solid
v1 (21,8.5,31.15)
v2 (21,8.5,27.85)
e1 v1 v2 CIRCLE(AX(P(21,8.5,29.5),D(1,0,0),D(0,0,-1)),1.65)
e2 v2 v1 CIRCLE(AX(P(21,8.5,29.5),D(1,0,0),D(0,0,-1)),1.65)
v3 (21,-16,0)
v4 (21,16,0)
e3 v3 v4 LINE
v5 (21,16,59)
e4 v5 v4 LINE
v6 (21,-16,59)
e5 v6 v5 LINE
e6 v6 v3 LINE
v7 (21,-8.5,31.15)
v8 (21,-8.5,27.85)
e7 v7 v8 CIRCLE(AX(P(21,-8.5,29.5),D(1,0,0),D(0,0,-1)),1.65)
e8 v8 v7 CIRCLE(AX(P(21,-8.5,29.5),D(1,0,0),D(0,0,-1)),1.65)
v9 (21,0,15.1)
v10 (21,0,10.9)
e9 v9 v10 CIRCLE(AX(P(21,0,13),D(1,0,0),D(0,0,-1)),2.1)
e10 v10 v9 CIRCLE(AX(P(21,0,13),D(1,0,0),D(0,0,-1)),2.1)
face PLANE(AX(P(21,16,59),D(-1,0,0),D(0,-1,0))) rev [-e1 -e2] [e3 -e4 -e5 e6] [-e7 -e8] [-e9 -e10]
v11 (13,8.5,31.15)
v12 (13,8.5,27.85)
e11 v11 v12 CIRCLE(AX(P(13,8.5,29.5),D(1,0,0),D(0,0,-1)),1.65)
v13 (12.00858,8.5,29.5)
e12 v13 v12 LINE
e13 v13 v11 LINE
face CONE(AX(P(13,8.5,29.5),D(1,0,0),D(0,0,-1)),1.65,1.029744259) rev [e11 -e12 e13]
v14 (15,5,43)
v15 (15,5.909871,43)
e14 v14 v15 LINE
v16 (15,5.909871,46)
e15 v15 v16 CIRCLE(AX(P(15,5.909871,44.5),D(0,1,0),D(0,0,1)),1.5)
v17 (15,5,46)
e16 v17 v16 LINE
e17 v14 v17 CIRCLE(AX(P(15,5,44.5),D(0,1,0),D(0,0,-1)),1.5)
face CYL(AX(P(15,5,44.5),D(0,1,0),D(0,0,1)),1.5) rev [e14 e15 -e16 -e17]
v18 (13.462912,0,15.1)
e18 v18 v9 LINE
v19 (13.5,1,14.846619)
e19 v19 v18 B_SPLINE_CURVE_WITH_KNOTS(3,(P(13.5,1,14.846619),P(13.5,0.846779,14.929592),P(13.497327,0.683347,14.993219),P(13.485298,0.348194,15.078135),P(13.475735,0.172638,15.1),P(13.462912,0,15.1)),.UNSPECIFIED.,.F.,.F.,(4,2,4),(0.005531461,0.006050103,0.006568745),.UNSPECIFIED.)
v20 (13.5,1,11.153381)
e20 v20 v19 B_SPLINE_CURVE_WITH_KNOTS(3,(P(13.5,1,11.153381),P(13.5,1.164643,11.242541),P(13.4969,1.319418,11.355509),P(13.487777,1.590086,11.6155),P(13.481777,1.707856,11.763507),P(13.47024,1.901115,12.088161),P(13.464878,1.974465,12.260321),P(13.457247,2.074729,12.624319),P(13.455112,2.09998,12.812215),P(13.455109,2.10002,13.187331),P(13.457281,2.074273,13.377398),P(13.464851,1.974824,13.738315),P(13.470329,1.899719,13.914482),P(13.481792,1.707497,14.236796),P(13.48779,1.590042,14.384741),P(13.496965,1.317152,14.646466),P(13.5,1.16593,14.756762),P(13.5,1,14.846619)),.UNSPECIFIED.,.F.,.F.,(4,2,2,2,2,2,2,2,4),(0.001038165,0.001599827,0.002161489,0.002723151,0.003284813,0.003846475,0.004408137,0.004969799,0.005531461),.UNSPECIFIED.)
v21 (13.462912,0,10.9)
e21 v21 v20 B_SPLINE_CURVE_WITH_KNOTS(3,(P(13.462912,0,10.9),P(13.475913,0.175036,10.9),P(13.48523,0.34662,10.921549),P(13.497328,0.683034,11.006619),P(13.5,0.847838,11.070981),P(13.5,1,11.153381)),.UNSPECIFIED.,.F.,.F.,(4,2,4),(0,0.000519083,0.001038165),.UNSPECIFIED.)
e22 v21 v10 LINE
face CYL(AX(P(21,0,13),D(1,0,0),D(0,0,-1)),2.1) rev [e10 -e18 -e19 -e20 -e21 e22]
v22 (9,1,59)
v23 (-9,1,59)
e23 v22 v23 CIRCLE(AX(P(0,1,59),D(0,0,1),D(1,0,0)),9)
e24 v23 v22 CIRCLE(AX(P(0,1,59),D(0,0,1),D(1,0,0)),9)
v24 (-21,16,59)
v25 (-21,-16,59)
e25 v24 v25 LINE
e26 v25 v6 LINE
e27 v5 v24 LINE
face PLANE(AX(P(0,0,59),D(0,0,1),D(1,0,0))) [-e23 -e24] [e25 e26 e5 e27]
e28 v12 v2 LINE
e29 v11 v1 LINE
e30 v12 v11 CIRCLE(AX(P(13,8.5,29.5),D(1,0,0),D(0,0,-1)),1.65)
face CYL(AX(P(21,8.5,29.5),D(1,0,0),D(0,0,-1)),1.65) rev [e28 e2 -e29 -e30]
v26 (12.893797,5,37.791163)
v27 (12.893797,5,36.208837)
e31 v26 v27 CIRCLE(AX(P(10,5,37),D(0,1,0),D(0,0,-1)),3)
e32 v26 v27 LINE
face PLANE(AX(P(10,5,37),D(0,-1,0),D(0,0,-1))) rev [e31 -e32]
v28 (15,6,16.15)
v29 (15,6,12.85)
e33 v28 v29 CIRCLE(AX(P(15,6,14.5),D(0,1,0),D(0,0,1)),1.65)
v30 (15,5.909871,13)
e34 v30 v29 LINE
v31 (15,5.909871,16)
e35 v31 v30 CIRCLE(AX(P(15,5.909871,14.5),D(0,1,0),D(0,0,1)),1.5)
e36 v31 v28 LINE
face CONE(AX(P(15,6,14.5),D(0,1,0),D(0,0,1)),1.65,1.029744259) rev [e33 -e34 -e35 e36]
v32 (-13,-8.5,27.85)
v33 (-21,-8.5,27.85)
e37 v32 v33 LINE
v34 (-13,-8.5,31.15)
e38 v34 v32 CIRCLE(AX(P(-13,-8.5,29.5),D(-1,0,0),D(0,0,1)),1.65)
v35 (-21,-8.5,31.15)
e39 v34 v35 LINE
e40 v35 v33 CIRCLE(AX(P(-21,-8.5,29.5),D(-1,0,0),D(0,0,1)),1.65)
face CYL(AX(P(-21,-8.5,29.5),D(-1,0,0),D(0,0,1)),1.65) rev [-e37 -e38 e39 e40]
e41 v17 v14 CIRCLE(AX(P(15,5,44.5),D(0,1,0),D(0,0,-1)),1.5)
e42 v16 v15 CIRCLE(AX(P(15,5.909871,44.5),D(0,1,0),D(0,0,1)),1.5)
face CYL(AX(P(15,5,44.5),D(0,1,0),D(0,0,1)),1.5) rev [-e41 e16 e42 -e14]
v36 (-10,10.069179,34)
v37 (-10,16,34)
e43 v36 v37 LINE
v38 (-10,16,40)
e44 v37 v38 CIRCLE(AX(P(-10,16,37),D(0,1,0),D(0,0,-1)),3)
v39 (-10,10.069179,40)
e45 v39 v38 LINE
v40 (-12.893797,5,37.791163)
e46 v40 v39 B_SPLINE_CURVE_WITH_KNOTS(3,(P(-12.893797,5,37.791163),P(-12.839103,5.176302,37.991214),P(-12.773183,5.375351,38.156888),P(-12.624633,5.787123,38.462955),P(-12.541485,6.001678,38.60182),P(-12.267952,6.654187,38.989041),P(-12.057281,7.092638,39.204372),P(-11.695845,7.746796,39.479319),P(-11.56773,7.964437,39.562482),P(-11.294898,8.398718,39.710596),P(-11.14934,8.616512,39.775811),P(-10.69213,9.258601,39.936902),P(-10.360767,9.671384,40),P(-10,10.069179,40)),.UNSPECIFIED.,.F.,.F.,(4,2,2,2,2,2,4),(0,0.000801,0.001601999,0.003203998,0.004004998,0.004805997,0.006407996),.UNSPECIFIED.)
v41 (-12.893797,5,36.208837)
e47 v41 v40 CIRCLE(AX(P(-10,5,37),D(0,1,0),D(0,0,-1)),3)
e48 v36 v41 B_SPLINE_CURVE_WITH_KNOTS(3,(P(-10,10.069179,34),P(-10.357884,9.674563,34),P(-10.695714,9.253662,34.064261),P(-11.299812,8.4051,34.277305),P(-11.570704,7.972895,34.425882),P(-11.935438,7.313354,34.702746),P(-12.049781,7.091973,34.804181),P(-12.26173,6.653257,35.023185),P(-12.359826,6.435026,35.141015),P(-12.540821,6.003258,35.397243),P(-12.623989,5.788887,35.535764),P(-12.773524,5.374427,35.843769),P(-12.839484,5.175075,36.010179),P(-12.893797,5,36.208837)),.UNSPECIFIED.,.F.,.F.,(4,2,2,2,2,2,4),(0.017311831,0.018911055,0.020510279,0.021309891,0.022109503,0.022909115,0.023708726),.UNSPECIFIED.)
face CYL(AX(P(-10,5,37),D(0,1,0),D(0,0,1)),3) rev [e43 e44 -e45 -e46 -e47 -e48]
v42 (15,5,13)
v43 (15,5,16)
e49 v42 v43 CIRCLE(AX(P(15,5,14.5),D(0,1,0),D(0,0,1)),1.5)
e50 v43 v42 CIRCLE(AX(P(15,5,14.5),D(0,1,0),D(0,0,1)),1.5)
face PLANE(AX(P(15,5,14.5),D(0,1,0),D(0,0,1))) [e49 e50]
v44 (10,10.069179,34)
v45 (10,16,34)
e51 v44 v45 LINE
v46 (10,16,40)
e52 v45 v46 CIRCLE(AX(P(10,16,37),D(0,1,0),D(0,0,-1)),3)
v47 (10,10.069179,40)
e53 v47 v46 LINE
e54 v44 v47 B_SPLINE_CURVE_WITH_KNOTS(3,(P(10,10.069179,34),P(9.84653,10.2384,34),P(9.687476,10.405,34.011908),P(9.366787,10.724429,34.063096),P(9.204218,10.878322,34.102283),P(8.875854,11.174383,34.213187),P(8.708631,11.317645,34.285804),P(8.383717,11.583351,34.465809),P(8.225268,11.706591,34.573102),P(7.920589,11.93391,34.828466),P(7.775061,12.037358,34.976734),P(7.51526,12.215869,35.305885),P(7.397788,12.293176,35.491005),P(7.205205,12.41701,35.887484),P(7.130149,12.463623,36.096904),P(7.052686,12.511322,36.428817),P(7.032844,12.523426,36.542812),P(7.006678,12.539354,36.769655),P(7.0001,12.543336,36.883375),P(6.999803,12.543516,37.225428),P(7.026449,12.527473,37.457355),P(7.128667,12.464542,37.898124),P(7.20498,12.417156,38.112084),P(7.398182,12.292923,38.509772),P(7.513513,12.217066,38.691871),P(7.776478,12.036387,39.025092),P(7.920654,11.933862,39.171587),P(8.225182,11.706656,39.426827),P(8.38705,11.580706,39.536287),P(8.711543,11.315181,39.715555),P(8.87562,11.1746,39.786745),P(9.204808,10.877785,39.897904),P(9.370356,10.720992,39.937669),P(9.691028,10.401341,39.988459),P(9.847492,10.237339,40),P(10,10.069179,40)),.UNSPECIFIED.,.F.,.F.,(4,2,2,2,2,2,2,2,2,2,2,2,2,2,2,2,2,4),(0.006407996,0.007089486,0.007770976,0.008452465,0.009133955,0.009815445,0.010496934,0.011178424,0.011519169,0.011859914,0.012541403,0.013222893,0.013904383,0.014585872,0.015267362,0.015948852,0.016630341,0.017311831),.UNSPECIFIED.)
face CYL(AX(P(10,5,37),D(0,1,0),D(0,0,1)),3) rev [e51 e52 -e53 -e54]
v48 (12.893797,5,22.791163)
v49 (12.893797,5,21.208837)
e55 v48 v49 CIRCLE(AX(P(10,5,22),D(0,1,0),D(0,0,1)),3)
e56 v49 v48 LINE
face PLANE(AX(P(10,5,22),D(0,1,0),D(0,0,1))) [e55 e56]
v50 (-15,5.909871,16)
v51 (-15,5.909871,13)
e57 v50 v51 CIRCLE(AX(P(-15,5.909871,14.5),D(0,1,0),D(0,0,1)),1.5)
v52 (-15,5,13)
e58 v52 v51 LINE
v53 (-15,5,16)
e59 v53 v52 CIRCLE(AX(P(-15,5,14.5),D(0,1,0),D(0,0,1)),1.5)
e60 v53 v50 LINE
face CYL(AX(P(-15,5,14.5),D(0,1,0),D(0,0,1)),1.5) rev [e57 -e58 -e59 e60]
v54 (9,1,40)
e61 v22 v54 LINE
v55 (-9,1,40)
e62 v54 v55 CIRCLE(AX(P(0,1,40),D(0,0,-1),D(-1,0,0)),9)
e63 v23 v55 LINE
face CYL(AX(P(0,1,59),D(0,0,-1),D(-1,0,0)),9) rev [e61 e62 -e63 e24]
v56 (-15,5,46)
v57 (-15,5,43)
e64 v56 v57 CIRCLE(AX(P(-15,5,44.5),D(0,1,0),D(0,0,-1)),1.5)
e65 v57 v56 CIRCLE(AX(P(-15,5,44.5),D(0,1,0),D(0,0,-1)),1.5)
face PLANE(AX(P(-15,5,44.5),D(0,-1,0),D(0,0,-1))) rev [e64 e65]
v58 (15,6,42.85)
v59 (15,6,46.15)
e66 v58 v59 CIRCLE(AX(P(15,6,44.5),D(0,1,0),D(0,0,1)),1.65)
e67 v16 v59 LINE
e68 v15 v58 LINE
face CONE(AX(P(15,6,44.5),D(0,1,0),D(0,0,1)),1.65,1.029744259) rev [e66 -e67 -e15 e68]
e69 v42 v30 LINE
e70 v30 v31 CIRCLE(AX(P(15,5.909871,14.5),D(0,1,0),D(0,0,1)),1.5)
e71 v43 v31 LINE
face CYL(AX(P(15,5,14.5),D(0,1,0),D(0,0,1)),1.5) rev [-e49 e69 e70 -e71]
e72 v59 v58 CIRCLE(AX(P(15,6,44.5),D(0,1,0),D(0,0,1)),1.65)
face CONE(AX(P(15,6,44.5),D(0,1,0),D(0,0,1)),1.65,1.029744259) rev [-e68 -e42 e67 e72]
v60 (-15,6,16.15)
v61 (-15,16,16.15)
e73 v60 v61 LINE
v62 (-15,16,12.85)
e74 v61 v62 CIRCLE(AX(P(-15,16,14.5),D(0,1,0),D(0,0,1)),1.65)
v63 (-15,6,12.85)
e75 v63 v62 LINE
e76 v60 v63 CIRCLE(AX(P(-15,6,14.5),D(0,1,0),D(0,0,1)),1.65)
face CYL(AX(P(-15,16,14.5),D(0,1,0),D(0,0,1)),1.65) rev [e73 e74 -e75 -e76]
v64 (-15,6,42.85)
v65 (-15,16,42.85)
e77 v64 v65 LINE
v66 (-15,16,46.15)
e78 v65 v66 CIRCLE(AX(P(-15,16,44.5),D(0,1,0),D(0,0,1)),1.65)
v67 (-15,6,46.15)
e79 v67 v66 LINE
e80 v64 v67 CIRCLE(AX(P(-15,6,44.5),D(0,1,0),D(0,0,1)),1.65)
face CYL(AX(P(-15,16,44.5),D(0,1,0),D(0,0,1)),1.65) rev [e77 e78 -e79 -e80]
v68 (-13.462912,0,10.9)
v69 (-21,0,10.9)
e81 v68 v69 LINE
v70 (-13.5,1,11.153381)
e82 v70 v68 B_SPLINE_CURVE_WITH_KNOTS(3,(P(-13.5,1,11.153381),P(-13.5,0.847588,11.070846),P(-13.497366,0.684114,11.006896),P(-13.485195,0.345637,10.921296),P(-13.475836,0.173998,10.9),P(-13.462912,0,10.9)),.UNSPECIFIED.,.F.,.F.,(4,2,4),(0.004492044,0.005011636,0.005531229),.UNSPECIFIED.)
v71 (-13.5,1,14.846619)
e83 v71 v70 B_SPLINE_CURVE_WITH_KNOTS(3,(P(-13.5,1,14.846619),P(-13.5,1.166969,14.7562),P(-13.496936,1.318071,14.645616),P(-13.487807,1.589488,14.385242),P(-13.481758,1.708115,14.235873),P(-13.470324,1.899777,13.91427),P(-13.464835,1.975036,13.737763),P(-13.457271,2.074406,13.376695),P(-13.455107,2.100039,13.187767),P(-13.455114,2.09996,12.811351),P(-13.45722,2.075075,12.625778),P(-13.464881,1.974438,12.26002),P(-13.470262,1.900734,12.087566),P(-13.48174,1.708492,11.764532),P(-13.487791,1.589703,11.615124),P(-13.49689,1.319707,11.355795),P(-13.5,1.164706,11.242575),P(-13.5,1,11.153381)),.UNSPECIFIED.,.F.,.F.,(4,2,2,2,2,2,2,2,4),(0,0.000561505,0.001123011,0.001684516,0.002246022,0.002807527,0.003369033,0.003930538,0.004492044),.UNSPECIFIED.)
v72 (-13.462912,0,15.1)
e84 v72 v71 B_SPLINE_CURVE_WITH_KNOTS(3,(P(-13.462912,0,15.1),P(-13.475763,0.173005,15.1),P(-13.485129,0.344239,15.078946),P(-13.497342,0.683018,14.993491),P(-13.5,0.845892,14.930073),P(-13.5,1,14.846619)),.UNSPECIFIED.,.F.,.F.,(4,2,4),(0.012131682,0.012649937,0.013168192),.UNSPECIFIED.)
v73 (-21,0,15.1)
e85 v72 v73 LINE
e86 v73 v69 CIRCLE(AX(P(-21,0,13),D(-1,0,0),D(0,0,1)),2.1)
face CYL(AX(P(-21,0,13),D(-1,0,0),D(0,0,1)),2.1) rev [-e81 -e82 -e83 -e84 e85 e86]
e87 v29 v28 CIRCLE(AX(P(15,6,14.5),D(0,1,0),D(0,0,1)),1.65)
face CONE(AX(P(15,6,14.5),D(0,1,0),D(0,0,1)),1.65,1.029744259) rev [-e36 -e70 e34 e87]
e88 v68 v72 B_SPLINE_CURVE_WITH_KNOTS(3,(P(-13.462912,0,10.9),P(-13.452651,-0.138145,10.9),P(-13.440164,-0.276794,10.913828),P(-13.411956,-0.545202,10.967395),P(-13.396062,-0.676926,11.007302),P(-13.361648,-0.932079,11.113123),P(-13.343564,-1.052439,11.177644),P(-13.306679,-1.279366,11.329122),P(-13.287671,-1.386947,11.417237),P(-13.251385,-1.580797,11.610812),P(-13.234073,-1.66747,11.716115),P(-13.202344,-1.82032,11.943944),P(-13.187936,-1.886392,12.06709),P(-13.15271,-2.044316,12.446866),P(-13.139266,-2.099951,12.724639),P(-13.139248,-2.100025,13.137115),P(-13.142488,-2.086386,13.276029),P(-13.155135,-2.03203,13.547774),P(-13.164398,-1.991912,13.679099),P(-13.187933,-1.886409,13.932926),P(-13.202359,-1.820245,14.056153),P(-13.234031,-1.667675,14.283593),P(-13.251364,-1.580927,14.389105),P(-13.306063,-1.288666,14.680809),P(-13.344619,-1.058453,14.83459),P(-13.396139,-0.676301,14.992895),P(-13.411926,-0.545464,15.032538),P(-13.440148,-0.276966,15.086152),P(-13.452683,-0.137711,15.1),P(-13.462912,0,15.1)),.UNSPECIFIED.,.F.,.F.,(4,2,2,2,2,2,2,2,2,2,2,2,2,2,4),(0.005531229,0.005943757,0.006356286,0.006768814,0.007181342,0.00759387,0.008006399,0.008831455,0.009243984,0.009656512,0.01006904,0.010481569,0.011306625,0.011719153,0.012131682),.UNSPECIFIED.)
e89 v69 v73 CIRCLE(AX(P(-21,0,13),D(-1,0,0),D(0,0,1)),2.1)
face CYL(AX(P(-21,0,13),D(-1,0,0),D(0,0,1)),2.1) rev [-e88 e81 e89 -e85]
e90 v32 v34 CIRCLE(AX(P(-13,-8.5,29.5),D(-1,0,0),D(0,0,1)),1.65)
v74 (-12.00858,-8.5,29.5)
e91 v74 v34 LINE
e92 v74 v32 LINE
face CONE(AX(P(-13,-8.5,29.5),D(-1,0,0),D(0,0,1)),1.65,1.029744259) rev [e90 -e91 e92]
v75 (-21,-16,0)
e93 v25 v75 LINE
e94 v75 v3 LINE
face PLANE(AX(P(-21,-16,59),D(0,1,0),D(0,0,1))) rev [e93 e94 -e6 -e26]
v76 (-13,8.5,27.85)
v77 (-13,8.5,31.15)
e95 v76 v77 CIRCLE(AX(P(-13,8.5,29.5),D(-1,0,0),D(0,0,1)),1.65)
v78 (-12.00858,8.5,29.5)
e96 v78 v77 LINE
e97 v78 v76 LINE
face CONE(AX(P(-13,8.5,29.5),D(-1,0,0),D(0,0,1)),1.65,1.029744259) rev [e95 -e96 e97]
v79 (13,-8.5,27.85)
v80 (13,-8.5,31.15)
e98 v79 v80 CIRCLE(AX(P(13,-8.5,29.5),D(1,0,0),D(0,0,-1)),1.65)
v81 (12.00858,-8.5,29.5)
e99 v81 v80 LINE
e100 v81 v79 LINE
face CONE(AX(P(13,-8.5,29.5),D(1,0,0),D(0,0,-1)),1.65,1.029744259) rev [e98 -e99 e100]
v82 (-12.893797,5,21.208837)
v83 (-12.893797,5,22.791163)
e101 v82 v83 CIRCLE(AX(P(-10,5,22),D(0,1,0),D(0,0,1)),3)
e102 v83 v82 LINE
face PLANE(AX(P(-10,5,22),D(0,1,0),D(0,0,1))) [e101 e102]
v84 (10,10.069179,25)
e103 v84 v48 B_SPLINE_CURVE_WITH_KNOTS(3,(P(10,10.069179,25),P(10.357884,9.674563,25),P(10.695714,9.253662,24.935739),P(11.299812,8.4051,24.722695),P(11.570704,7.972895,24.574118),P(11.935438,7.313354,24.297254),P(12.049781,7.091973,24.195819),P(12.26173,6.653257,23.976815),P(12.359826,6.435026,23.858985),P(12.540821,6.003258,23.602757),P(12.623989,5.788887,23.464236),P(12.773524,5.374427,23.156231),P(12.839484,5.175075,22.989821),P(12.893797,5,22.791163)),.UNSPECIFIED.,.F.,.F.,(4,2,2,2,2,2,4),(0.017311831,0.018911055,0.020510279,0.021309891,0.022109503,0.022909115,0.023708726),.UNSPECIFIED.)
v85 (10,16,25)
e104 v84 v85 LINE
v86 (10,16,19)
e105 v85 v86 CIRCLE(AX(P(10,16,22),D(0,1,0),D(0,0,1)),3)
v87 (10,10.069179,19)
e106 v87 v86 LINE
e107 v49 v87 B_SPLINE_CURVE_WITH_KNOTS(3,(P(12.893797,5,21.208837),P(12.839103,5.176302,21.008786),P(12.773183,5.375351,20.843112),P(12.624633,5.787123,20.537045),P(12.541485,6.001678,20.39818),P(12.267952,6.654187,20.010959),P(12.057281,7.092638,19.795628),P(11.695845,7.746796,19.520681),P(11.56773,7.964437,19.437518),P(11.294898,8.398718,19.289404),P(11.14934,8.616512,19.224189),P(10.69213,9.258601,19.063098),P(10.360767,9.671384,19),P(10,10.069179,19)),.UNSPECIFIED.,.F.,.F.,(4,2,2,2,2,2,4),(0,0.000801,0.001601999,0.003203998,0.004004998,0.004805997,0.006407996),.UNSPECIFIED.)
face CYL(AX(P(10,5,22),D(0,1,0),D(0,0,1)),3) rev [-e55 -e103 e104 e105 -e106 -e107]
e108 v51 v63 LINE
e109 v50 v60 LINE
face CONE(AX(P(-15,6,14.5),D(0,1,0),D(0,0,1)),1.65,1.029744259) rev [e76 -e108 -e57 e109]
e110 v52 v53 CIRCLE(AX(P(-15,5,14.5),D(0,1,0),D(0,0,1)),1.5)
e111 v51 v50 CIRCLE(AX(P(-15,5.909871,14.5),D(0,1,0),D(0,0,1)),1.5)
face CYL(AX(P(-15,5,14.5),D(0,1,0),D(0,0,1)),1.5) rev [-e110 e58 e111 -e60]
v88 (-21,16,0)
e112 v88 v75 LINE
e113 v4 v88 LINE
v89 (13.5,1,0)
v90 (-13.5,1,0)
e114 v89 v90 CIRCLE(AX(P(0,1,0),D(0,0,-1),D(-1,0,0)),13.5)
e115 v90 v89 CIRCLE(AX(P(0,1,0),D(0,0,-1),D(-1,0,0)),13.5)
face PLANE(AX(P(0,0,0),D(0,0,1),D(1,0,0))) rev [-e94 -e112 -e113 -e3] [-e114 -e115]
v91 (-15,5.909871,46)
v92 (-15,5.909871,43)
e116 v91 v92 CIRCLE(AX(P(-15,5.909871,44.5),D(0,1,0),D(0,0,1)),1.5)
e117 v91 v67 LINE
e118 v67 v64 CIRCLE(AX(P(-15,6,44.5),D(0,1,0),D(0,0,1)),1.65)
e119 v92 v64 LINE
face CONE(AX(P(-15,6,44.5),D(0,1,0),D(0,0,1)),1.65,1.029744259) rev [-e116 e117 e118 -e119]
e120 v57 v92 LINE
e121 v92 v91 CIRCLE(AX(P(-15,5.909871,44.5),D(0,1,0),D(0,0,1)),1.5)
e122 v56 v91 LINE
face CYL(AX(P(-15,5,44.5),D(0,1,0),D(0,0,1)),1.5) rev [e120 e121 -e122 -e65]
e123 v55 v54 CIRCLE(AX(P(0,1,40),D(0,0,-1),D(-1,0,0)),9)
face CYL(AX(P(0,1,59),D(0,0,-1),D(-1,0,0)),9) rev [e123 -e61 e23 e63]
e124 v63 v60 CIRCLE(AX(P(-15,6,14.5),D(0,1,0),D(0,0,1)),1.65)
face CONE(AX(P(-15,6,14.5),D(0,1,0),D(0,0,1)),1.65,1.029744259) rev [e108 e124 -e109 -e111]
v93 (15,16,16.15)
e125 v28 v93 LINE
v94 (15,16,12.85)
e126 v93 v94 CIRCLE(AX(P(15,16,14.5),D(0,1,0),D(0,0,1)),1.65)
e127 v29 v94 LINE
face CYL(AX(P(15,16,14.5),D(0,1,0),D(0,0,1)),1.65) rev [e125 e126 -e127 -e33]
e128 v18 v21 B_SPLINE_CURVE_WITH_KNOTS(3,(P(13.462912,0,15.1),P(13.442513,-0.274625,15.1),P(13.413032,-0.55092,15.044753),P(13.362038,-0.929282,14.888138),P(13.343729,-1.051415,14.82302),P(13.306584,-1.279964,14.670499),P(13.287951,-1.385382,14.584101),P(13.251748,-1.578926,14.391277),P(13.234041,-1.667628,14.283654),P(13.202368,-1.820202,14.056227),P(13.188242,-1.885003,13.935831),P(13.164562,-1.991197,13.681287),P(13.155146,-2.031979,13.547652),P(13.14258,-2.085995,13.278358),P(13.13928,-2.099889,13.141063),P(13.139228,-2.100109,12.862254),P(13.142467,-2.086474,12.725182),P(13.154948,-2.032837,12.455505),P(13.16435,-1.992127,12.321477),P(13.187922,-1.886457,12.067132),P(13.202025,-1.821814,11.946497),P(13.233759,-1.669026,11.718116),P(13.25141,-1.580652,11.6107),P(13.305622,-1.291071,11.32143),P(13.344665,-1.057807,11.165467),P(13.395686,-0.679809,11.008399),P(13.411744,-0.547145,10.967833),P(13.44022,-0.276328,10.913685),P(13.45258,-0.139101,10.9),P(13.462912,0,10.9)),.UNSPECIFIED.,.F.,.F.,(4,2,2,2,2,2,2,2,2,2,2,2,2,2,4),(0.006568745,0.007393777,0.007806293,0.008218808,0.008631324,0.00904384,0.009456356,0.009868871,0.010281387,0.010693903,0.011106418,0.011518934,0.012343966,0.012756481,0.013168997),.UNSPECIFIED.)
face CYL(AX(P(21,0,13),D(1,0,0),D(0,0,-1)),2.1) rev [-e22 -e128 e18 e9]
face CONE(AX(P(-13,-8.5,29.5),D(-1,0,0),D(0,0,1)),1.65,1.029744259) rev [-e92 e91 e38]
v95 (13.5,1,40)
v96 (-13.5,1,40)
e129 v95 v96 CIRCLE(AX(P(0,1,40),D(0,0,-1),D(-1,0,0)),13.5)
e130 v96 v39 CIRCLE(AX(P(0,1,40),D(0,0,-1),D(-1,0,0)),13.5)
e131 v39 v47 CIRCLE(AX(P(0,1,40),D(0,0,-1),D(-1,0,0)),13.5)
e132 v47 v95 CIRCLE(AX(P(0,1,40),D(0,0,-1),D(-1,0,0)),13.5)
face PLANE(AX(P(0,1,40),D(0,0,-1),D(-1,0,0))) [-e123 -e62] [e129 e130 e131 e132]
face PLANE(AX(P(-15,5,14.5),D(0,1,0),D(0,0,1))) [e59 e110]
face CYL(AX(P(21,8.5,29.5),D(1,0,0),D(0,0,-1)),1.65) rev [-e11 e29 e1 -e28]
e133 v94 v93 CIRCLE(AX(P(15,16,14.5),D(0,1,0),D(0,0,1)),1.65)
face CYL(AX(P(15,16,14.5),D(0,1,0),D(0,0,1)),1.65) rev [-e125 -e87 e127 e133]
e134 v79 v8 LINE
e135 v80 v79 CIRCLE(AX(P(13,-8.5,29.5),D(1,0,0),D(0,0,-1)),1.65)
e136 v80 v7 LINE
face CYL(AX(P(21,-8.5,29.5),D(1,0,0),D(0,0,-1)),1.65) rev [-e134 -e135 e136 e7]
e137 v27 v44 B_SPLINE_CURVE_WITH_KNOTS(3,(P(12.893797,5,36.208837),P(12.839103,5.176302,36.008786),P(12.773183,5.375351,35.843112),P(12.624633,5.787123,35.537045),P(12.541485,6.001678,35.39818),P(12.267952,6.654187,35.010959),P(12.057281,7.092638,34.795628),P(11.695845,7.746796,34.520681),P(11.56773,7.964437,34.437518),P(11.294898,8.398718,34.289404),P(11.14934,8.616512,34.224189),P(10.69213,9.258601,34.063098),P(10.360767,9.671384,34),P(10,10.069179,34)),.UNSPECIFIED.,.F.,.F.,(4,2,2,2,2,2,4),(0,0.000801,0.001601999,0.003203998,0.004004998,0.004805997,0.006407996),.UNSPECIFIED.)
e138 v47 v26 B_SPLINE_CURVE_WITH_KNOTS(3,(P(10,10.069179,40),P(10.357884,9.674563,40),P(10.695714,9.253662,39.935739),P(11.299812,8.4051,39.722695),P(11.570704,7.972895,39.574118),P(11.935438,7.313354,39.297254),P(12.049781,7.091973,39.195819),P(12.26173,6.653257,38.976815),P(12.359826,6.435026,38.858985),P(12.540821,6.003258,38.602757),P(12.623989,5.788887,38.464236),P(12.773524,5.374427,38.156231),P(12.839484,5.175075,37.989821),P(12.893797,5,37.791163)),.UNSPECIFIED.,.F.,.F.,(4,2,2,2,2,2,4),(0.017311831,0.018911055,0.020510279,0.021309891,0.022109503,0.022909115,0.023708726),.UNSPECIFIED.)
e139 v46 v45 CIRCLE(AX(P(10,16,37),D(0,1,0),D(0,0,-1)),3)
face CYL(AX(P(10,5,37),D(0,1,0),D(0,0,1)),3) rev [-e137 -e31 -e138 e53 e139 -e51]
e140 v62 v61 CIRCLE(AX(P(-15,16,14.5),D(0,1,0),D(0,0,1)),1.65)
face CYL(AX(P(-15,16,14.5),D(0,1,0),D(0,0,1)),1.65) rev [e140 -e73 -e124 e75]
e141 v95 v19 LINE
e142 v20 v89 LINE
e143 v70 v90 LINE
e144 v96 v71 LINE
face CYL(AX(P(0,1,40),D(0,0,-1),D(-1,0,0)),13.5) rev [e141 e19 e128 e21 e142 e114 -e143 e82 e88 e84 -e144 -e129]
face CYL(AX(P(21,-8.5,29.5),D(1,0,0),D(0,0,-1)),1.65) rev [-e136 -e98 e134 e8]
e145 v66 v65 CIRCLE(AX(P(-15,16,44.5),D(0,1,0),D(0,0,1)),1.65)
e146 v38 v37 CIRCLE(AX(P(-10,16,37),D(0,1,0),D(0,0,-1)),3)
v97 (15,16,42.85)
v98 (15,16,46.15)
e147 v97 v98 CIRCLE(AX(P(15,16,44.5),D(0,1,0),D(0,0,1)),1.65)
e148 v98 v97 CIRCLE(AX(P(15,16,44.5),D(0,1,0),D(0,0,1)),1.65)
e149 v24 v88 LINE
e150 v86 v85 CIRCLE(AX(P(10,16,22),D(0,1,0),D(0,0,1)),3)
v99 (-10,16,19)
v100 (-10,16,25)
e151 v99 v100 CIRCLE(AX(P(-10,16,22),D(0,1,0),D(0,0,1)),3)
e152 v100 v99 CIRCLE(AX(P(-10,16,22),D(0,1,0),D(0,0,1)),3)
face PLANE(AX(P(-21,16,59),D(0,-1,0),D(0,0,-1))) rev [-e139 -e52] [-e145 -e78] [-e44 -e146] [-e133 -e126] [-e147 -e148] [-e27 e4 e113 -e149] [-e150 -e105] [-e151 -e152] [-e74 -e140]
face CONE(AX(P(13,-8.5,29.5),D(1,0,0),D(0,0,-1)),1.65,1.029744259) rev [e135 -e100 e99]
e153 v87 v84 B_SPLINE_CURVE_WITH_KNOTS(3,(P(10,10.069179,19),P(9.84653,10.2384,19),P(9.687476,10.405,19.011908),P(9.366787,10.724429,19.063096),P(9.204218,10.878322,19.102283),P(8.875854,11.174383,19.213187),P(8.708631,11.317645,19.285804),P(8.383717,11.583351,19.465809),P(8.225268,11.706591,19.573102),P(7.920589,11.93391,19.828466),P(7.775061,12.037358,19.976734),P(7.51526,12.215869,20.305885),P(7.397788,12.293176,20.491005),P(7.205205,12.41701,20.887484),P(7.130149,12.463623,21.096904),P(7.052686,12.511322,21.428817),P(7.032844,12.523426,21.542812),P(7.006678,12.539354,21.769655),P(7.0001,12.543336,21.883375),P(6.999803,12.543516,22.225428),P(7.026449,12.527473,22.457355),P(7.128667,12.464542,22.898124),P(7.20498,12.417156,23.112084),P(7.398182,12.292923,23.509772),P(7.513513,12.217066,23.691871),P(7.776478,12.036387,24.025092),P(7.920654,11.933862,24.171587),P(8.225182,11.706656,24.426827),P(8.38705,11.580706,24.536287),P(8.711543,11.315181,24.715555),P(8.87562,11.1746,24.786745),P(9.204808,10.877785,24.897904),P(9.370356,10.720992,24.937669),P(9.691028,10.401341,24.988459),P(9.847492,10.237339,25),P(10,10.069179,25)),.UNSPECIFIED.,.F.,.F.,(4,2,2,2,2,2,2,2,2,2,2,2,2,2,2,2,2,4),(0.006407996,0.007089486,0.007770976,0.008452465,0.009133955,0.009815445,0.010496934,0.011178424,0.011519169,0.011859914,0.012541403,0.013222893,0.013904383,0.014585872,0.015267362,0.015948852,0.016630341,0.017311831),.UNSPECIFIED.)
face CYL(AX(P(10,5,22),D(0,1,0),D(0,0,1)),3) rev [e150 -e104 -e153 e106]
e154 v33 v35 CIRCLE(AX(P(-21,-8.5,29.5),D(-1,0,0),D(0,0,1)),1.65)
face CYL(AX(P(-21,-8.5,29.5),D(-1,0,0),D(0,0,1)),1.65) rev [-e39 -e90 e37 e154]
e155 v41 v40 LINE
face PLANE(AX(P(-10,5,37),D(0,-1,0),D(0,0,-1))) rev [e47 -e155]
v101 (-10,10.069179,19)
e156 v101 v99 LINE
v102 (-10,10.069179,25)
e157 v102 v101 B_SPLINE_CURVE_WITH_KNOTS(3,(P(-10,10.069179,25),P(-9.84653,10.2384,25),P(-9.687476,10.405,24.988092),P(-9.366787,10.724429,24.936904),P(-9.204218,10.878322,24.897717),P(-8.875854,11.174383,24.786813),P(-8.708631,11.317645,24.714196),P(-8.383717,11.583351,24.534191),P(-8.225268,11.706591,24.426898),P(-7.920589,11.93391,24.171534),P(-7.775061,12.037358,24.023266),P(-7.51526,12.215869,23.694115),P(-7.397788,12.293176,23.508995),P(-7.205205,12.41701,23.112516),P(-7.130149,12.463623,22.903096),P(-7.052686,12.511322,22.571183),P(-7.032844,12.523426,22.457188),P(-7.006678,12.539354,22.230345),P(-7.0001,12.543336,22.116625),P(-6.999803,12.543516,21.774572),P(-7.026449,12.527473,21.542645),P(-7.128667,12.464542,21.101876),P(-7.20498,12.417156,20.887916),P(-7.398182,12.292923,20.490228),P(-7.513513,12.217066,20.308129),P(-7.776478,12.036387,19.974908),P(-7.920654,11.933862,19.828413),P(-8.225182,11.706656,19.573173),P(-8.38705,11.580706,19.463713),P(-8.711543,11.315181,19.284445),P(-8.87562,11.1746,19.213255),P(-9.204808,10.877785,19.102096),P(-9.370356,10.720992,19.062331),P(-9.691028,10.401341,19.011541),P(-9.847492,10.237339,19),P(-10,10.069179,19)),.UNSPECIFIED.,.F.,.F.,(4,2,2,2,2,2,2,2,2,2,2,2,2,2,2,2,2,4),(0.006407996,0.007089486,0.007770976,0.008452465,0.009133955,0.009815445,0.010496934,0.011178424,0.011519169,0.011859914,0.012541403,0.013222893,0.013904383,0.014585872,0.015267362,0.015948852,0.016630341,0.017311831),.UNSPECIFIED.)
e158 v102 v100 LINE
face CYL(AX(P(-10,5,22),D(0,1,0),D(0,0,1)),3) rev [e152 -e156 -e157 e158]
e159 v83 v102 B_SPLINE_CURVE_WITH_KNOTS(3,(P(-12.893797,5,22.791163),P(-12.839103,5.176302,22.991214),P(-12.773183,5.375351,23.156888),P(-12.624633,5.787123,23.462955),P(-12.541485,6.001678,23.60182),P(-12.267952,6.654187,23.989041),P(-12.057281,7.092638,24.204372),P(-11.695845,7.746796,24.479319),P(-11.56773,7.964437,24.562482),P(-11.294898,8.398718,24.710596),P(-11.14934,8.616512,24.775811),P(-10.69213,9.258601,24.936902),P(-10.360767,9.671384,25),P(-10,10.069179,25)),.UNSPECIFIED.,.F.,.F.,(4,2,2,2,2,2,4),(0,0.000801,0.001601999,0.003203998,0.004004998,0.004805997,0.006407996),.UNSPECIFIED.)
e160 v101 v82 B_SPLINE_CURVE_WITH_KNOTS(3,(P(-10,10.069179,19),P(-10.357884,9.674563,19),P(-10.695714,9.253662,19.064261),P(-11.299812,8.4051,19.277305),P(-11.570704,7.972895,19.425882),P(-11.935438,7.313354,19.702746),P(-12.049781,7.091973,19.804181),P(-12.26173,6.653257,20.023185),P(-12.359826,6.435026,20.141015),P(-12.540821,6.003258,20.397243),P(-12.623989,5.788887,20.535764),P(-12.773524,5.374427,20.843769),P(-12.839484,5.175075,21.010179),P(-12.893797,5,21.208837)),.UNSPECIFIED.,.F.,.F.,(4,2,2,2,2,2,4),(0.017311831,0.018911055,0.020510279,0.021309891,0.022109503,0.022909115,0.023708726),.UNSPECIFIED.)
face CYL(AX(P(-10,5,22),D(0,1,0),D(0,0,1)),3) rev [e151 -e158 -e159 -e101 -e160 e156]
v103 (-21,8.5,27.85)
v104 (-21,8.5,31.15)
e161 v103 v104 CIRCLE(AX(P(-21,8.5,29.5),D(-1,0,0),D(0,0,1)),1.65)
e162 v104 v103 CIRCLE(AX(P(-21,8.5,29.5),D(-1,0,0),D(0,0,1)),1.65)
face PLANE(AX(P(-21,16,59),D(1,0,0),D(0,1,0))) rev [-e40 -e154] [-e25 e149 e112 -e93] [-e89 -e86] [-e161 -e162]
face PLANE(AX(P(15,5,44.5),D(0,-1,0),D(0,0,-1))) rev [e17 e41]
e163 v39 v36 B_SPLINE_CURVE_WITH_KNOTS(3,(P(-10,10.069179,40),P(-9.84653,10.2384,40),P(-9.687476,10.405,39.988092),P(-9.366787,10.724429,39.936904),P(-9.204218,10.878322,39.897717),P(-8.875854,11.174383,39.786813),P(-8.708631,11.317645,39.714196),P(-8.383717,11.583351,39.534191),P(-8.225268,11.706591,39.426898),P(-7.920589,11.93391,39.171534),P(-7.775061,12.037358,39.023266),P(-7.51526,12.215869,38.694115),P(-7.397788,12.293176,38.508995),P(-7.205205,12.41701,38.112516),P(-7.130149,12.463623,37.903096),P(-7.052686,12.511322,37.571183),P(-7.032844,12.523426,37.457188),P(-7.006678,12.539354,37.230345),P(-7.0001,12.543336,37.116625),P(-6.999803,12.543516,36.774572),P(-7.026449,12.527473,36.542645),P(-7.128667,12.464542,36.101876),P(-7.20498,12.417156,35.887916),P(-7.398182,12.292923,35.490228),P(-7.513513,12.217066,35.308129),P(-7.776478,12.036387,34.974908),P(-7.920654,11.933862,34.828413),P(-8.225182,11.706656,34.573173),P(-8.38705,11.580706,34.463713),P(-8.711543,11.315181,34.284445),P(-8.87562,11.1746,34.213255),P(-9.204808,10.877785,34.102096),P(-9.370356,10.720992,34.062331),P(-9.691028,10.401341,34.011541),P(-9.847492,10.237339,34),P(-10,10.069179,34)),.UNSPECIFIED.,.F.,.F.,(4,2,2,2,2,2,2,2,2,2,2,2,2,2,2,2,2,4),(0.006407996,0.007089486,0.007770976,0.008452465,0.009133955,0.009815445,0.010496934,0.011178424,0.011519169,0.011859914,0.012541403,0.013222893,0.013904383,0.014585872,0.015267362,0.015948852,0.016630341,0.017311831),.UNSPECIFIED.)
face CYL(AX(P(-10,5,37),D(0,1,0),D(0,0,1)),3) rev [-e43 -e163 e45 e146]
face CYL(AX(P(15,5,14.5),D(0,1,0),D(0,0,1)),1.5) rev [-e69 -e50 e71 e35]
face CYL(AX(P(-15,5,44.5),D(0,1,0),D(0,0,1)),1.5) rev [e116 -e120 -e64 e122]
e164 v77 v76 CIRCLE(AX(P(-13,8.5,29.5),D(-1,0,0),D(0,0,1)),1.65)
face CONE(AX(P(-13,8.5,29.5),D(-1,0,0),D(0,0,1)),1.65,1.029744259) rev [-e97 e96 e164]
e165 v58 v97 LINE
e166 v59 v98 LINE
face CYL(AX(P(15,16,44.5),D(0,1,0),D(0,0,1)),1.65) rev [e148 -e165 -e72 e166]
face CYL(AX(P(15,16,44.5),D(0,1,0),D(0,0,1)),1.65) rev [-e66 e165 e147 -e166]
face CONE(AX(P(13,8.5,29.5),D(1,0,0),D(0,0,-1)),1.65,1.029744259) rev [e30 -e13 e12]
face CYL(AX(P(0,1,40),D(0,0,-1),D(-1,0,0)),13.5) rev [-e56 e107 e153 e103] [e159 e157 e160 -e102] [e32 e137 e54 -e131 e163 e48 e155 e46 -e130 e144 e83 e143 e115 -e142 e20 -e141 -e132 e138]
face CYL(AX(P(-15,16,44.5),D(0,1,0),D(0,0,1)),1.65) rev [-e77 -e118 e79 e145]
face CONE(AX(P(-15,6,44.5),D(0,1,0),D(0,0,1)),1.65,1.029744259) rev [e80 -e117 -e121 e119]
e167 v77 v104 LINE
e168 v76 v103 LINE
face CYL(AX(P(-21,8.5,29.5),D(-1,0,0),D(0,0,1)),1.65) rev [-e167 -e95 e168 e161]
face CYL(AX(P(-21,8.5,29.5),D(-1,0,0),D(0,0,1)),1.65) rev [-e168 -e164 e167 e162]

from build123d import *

# Parameters (mm, degrees)
SKETCH1_W                  = 42
SKETCH1_H                  = 32
SKETCH1_R                  = 9
BOSS_EXTRUDE1_DEPTH        = 59
SKETCH2_R                  = 13.5
CUT_EXTRUDE1_DEPTH         = 40
M4_TAPPED_HOLE1_AT_2_COUNT = 2
M4_TAPPED_HOLE1_AT_2_PITCH = 17
SKETCH8_R                  = 1.5
SKETCH8_R_2                = 3
CUT_EXTRUDE2_DEPTH         = 11
M4_TAPPED_HOLE2_D          = 3.3
M4_TAPPED_HOLE2_DEPTH      = 10
M4_TAPPED_HOLE2_TIP        = 0.991420021


with BuildPart() as part:
    # Sketch1 → Boss-Extrude1 (new body)
    with BuildSketch(Plane.XY):
        Rectangle(SKETCH1_W, SKETCH1_H)
        with Locations((0, 1)):
            Circle(SKETCH1_R, mode=Mode.SUBTRACT)
    extrude(amount=BOSS_EXTRUDE1_DEPTH)

    # Sketch2 → Cut-Extrude1 (cut)
    with BuildSketch(Plane(origin=(0, 0, 0), x_dir=(-1, 0, 0), z_dir=(0, 0, -1))):
        with Locations((0, 1)):
            Circle(SKETCH2_R)
    extrude(amount=-CUT_EXTRUDE1_DEPTH, mode=Mode.SUBTRACT)

    # Sketch4 → M4 Tapped Hole1 (revolve, cut)
    with BuildSketch(Plane(origin=(-21, 8.5, 29.5), x_dir=(0, 0, 1), z_dir=(0, 1, 0))):
        Polygon((0, 0), (0, 8.991420021), (1.65, 8), (1.65, 0), align=None)
    m4_tapped_hole1 = revolve(axis=Axis((-27.35, 8.5, 29.5), (1, 0, 0)), mode=Mode.SUBTRACT)

    # M4 Tapped Hole1 at 2: M4 Tapped Hole1 ×2
    with Locations(*[(0, -i * M4_TAPPED_HOLE1_AT_2_PITCH, 0) for i in range(1, M4_TAPPED_HOLE1_AT_2_COUNT)]):
        add(m4_tapped_hole1, mode=Mode.SUBTRACT)

    # Sketch6 → M5 Tapped Hole1 (revolve, cut)
    with BuildSketch(Plane(origin=(-21, 0, 13), x_dir=(0, 0, 1), z_dir=(0, 1, 0))):
        Polygon((0, 0), (0, 15.2618073), (2.1, 14), (2.1, 0), align=None)
    m5_tapped_hole1 = revolve(axis=Axis((-27.35, 0, 13), (1, 0, 0)), mode=Mode.SUBTRACT)

    # Mirror1: M4 Tapped Hole1, M5 Tapped Hole1 across plane
    add(m4_tapped_hole1.mirror(Plane(origin=(0, 0, 0), x_dir=(0, 0, 1), z_dir=(1, 0, 0))), mode=Mode.SUBTRACT)
    add(m5_tapped_hole1.mirror(Plane(origin=(0, 0, 0), x_dir=(0, 0, 1), z_dir=(1, 0, 0))), mode=Mode.SUBTRACT)

    # Mirror1 copy 1 sketch → Mirror1 copy 1 (revolve, cut)
    with BuildSketch(Plane(origin=(21, -8.5, 29.5), x_dir=(0, 0, 1), z_dir=(0, 1, 0))):
        Polygon((0, 0), (0, -8.991420021), (1.65, -8), (1.65, 0), align=None)
    revolve(axis=Axis((27.35, -8.5, 29.5), (1, 0, 0)), mode=Mode.SUBTRACT)

    # Sketch8 → Cut-Extrude2 (cut)
    with BuildSketch(Plane(origin=(0, 16, 0), x_dir=(1, 0, 0), z_dir=(0, 1, 0))):
        with Locations(Location((-15, -14.5, 0), (0, 0, 270))):
            Circle(SKETCH8_R)
        with Locations(Location((-10, -22, 0), (0, 0, 270))):
            Circle(SKETCH8_R_2)
        with Locations(Location((10, -22, 0), (0, 0, 270))):
            Circle(SKETCH8_R_2)
        with Locations(Location((15, -14.5, 0), (0, 0, 270))):
            Circle(SKETCH8_R)
        with Locations(Location((15, -44.5, 0), (0, 0, 90))):
            Circle(SKETCH8_R)
        with Locations(Location((10, -37, 0), (0, 0, 269.999992681))):
            Circle(SKETCH8_R_2)
        with Locations(Location((-10, -37, 0), (0, 0, 269.999954887))):
            Circle(SKETCH8_R_2)
        with Locations(Location((-15, -44.5, 0), (0, 0, 90))):
            Circle(SKETCH8_R)
    extrude(amount=-CUT_EXTRUDE2_DEPTH, mode=Mode.SUBTRACT)

    # M4 Tapped Hole2
    with Locations(Plane(origin=(0, 16, 0), x_dir=(1, 0, 0), z_dir=(0, 1, 0))):
        with Locations((15, -14.5), (15, -44.5), (-15, -44.5), (-15, -14.5)):
            Hole(M4_TAPPED_HOLE2_D / 2, depth=M4_TAPPED_HOLE2_DEPTH)
            with Locations((0, 0, -(M4_TAPPED_HOLE2_DEPTH + M4_TAPPED_HOLE2_TIP / 2))):  # 118° drill point
                Cone(0, M4_TAPPED_HOLE2_D / 2, M4_TAPPED_HOLE2_TIP, mode=Mode.SUBTRACT)


solid = part.part
